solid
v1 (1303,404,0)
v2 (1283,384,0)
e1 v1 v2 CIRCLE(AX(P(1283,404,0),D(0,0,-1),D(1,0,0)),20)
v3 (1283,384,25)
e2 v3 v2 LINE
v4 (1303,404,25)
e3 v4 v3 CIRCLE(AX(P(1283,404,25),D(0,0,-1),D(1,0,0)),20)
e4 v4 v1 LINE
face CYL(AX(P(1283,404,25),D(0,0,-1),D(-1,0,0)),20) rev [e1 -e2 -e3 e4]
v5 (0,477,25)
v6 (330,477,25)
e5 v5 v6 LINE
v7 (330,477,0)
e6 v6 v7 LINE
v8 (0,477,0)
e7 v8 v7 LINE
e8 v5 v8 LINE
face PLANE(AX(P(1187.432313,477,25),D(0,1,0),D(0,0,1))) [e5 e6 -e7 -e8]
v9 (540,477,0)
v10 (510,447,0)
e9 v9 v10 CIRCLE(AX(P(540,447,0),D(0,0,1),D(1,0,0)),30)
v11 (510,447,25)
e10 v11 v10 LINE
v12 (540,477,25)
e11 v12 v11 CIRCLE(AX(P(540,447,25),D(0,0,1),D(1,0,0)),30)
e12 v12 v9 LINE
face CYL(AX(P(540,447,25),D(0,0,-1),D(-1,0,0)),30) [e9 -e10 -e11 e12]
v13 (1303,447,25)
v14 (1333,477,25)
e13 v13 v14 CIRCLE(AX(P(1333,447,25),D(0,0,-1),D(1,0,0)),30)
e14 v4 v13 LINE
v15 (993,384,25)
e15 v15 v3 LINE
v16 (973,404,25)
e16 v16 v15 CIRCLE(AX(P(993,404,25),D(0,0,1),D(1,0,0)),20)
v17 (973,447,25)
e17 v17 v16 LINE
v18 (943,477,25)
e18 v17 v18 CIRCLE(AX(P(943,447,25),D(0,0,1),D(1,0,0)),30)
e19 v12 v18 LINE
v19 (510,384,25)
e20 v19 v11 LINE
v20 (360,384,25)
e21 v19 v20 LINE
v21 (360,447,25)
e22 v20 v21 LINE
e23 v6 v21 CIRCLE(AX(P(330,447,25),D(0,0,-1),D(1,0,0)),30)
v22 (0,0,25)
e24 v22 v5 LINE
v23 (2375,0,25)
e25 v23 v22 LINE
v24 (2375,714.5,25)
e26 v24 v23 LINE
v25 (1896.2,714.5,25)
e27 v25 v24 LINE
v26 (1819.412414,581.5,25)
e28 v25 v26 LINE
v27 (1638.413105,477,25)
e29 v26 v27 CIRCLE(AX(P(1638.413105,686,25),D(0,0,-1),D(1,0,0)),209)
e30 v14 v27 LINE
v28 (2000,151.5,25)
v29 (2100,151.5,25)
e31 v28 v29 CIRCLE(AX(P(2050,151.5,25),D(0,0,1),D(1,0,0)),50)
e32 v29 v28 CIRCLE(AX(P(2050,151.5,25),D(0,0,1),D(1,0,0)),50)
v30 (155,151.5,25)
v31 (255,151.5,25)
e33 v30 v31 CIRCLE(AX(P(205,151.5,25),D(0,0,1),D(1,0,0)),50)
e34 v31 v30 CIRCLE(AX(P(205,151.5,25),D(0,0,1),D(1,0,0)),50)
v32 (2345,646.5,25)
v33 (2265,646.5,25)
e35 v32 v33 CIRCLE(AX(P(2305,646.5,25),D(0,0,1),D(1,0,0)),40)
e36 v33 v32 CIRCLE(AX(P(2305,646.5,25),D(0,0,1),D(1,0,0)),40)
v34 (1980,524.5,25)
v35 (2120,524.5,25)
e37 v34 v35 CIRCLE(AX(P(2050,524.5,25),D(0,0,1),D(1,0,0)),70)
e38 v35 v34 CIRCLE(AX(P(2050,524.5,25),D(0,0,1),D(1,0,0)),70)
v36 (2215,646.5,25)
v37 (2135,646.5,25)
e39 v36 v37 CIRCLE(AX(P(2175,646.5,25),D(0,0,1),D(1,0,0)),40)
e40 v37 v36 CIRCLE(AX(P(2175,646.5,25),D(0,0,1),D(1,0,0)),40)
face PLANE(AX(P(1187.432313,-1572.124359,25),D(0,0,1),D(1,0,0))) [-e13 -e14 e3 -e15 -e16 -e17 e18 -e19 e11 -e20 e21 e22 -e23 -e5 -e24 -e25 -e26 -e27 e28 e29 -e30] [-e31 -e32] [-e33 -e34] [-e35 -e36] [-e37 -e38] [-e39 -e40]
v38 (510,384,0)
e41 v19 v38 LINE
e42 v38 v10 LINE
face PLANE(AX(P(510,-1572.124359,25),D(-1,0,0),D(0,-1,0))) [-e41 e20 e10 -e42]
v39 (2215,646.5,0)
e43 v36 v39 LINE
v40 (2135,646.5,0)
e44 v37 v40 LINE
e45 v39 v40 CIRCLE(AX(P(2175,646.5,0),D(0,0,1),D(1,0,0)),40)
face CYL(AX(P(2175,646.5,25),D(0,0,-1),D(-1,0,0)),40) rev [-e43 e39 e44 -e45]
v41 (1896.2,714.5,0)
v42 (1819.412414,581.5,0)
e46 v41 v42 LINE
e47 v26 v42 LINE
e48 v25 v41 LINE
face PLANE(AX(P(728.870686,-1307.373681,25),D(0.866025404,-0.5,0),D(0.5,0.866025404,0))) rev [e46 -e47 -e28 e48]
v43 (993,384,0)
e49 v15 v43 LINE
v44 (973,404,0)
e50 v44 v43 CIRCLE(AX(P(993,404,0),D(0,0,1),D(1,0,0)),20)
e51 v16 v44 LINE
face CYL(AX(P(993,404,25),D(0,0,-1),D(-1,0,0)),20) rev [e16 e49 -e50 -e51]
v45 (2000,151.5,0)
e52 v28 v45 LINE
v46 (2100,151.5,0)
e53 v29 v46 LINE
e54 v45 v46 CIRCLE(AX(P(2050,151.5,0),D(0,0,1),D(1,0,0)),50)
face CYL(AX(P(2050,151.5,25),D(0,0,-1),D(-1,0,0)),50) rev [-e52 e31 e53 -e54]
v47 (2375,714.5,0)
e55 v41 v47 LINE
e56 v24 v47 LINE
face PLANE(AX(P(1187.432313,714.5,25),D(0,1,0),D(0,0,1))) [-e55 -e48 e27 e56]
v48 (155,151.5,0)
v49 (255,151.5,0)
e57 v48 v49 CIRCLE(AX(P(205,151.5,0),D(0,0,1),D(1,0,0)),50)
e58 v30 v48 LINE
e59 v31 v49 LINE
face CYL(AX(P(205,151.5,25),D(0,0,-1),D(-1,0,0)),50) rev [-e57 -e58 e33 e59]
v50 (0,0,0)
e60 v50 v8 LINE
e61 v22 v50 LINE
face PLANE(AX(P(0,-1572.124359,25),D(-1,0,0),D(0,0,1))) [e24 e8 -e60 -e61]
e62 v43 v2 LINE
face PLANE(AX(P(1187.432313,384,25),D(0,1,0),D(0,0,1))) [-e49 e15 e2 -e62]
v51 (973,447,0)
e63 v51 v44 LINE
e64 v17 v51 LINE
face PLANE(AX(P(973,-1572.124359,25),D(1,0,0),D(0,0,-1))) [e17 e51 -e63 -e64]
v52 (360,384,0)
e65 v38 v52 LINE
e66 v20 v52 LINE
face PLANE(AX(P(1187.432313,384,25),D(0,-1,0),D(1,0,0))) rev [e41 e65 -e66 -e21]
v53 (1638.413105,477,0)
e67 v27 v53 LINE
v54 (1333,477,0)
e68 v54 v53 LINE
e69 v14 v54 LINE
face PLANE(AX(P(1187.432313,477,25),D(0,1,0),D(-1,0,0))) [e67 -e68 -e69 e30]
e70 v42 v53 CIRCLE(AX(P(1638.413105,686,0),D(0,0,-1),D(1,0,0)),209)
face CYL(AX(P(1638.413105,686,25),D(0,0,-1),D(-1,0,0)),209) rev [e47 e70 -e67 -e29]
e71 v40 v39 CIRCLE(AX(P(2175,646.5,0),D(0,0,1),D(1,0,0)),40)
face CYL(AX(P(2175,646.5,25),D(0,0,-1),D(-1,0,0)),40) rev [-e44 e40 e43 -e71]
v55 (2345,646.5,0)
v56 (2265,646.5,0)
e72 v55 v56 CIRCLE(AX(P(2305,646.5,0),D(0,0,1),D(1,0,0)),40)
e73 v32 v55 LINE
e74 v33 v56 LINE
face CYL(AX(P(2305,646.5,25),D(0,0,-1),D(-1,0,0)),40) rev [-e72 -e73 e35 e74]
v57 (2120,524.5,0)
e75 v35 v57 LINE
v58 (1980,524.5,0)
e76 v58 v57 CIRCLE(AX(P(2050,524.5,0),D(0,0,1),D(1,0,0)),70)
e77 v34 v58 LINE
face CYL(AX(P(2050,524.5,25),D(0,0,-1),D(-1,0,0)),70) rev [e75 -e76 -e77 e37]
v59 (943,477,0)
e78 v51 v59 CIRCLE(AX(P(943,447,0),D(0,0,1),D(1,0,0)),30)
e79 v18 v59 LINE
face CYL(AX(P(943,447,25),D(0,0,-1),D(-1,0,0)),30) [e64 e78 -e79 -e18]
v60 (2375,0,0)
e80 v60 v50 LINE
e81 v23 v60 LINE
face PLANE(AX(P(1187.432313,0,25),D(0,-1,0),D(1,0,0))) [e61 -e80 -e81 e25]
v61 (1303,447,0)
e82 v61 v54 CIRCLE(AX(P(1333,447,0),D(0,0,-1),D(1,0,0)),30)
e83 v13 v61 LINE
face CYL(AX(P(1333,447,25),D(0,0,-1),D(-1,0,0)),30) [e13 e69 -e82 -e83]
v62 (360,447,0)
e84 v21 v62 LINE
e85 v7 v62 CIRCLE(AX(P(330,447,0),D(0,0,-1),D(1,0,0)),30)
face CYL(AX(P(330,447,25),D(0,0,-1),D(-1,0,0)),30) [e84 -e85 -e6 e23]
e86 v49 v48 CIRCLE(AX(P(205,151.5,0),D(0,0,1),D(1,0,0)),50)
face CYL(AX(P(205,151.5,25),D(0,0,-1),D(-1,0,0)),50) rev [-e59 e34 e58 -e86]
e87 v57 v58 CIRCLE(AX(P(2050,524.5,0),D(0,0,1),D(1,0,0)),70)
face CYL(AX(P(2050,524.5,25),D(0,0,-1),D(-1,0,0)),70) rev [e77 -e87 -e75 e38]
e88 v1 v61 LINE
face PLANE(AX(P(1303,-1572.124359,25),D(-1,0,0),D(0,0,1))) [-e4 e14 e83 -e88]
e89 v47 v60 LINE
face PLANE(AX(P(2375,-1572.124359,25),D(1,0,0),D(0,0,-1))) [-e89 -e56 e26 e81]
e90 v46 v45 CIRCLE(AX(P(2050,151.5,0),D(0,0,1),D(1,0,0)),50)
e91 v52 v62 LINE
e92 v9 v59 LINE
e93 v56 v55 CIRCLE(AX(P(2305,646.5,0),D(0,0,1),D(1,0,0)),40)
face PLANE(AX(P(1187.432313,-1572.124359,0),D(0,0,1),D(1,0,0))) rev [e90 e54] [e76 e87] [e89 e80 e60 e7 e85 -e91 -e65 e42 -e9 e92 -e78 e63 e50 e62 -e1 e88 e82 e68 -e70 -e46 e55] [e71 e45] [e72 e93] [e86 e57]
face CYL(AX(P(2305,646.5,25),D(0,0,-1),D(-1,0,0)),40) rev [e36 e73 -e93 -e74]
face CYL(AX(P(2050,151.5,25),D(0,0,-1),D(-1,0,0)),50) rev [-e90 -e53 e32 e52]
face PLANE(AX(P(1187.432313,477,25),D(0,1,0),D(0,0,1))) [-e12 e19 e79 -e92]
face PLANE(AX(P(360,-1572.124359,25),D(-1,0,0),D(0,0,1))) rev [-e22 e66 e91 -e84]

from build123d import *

# Parameters (mm, degrees)
SKETCH1_R           = 50
SKETCH1_R_2         = 70
SKETCH1_R_3         = 40
BOSS_EXTRUDE1_DEPTH = 25


with BuildPart() as part:
    # Sketch1 → Boss-Extrude1 (new body)
    with BuildSketch(Plane.XY):
        with BuildLine():
            Line((0, 0), (0, 477))
            Line((0, 477), (330, 477))
            ThreePointArc((330, 477), (351.213203436, 468.213203436), (360, 447))
            Line((360, 447), (360, 384))
            Line((360, 384), (510, 384))
            Line((510, 384), (510, 447))
            ThreePointArc((510, 447), (518.786796564, 468.213203436), (540, 477))
            Line((540, 477), (943, 477))
            ThreePointArc((943, 477), (964.213203436, 468.213203436), (973, 447))
            Line((973, 447), (973, 404))
            ThreePointArc((973, 404), (978.857864376, 389.857864376), (993, 384))
            Line((993, 384), (1283, 384))
            ThreePointArc((1283, 384), (1297.142135624, 389.857864376), (1303, 404))
            Line((1303, 404), (1303, 447))
            ThreePointArc((1303, 447), (1311.786796564, 468.213203436), (1333, 477))
            Line((1333, 477), (1638.413104807, 477))
            ThreePointArc((1638.413104807, 477), (1742.913104807, 505.000690609), (1819.412414198, 581.5))
            Line((1819.412414198, 581.5), (1896.2, 714.5))
            Line((1896.2, 714.5), (2375, 714.5))
            Line((2375, 714.5), (2375, 0))
            Line((2375, 0), (0, 0))
        make_face()
        with Locations((205, 151.5)):
            Circle(SKETCH1_R, mode=Mode.SUBTRACT)
        with Locations((2050, 151.5)):
            Circle(SKETCH1_R, mode=Mode.SUBTRACT)
        with Locations((2050, 524.5)):
            Circle(SKETCH1_R_2, mode=Mode.SUBTRACT)
        with Locations((2305, 646.5)):
            Circle(SKETCH1_R_3, mode=Mode.SUBTRACT)
        with Locations((2175, 646.5)):
            Circle(SKETCH1_R_3, mode=Mode.SUBTRACT)
    extrude(amount=BOSS_EXTRUDE1_DEPTH)


solid = part.part
